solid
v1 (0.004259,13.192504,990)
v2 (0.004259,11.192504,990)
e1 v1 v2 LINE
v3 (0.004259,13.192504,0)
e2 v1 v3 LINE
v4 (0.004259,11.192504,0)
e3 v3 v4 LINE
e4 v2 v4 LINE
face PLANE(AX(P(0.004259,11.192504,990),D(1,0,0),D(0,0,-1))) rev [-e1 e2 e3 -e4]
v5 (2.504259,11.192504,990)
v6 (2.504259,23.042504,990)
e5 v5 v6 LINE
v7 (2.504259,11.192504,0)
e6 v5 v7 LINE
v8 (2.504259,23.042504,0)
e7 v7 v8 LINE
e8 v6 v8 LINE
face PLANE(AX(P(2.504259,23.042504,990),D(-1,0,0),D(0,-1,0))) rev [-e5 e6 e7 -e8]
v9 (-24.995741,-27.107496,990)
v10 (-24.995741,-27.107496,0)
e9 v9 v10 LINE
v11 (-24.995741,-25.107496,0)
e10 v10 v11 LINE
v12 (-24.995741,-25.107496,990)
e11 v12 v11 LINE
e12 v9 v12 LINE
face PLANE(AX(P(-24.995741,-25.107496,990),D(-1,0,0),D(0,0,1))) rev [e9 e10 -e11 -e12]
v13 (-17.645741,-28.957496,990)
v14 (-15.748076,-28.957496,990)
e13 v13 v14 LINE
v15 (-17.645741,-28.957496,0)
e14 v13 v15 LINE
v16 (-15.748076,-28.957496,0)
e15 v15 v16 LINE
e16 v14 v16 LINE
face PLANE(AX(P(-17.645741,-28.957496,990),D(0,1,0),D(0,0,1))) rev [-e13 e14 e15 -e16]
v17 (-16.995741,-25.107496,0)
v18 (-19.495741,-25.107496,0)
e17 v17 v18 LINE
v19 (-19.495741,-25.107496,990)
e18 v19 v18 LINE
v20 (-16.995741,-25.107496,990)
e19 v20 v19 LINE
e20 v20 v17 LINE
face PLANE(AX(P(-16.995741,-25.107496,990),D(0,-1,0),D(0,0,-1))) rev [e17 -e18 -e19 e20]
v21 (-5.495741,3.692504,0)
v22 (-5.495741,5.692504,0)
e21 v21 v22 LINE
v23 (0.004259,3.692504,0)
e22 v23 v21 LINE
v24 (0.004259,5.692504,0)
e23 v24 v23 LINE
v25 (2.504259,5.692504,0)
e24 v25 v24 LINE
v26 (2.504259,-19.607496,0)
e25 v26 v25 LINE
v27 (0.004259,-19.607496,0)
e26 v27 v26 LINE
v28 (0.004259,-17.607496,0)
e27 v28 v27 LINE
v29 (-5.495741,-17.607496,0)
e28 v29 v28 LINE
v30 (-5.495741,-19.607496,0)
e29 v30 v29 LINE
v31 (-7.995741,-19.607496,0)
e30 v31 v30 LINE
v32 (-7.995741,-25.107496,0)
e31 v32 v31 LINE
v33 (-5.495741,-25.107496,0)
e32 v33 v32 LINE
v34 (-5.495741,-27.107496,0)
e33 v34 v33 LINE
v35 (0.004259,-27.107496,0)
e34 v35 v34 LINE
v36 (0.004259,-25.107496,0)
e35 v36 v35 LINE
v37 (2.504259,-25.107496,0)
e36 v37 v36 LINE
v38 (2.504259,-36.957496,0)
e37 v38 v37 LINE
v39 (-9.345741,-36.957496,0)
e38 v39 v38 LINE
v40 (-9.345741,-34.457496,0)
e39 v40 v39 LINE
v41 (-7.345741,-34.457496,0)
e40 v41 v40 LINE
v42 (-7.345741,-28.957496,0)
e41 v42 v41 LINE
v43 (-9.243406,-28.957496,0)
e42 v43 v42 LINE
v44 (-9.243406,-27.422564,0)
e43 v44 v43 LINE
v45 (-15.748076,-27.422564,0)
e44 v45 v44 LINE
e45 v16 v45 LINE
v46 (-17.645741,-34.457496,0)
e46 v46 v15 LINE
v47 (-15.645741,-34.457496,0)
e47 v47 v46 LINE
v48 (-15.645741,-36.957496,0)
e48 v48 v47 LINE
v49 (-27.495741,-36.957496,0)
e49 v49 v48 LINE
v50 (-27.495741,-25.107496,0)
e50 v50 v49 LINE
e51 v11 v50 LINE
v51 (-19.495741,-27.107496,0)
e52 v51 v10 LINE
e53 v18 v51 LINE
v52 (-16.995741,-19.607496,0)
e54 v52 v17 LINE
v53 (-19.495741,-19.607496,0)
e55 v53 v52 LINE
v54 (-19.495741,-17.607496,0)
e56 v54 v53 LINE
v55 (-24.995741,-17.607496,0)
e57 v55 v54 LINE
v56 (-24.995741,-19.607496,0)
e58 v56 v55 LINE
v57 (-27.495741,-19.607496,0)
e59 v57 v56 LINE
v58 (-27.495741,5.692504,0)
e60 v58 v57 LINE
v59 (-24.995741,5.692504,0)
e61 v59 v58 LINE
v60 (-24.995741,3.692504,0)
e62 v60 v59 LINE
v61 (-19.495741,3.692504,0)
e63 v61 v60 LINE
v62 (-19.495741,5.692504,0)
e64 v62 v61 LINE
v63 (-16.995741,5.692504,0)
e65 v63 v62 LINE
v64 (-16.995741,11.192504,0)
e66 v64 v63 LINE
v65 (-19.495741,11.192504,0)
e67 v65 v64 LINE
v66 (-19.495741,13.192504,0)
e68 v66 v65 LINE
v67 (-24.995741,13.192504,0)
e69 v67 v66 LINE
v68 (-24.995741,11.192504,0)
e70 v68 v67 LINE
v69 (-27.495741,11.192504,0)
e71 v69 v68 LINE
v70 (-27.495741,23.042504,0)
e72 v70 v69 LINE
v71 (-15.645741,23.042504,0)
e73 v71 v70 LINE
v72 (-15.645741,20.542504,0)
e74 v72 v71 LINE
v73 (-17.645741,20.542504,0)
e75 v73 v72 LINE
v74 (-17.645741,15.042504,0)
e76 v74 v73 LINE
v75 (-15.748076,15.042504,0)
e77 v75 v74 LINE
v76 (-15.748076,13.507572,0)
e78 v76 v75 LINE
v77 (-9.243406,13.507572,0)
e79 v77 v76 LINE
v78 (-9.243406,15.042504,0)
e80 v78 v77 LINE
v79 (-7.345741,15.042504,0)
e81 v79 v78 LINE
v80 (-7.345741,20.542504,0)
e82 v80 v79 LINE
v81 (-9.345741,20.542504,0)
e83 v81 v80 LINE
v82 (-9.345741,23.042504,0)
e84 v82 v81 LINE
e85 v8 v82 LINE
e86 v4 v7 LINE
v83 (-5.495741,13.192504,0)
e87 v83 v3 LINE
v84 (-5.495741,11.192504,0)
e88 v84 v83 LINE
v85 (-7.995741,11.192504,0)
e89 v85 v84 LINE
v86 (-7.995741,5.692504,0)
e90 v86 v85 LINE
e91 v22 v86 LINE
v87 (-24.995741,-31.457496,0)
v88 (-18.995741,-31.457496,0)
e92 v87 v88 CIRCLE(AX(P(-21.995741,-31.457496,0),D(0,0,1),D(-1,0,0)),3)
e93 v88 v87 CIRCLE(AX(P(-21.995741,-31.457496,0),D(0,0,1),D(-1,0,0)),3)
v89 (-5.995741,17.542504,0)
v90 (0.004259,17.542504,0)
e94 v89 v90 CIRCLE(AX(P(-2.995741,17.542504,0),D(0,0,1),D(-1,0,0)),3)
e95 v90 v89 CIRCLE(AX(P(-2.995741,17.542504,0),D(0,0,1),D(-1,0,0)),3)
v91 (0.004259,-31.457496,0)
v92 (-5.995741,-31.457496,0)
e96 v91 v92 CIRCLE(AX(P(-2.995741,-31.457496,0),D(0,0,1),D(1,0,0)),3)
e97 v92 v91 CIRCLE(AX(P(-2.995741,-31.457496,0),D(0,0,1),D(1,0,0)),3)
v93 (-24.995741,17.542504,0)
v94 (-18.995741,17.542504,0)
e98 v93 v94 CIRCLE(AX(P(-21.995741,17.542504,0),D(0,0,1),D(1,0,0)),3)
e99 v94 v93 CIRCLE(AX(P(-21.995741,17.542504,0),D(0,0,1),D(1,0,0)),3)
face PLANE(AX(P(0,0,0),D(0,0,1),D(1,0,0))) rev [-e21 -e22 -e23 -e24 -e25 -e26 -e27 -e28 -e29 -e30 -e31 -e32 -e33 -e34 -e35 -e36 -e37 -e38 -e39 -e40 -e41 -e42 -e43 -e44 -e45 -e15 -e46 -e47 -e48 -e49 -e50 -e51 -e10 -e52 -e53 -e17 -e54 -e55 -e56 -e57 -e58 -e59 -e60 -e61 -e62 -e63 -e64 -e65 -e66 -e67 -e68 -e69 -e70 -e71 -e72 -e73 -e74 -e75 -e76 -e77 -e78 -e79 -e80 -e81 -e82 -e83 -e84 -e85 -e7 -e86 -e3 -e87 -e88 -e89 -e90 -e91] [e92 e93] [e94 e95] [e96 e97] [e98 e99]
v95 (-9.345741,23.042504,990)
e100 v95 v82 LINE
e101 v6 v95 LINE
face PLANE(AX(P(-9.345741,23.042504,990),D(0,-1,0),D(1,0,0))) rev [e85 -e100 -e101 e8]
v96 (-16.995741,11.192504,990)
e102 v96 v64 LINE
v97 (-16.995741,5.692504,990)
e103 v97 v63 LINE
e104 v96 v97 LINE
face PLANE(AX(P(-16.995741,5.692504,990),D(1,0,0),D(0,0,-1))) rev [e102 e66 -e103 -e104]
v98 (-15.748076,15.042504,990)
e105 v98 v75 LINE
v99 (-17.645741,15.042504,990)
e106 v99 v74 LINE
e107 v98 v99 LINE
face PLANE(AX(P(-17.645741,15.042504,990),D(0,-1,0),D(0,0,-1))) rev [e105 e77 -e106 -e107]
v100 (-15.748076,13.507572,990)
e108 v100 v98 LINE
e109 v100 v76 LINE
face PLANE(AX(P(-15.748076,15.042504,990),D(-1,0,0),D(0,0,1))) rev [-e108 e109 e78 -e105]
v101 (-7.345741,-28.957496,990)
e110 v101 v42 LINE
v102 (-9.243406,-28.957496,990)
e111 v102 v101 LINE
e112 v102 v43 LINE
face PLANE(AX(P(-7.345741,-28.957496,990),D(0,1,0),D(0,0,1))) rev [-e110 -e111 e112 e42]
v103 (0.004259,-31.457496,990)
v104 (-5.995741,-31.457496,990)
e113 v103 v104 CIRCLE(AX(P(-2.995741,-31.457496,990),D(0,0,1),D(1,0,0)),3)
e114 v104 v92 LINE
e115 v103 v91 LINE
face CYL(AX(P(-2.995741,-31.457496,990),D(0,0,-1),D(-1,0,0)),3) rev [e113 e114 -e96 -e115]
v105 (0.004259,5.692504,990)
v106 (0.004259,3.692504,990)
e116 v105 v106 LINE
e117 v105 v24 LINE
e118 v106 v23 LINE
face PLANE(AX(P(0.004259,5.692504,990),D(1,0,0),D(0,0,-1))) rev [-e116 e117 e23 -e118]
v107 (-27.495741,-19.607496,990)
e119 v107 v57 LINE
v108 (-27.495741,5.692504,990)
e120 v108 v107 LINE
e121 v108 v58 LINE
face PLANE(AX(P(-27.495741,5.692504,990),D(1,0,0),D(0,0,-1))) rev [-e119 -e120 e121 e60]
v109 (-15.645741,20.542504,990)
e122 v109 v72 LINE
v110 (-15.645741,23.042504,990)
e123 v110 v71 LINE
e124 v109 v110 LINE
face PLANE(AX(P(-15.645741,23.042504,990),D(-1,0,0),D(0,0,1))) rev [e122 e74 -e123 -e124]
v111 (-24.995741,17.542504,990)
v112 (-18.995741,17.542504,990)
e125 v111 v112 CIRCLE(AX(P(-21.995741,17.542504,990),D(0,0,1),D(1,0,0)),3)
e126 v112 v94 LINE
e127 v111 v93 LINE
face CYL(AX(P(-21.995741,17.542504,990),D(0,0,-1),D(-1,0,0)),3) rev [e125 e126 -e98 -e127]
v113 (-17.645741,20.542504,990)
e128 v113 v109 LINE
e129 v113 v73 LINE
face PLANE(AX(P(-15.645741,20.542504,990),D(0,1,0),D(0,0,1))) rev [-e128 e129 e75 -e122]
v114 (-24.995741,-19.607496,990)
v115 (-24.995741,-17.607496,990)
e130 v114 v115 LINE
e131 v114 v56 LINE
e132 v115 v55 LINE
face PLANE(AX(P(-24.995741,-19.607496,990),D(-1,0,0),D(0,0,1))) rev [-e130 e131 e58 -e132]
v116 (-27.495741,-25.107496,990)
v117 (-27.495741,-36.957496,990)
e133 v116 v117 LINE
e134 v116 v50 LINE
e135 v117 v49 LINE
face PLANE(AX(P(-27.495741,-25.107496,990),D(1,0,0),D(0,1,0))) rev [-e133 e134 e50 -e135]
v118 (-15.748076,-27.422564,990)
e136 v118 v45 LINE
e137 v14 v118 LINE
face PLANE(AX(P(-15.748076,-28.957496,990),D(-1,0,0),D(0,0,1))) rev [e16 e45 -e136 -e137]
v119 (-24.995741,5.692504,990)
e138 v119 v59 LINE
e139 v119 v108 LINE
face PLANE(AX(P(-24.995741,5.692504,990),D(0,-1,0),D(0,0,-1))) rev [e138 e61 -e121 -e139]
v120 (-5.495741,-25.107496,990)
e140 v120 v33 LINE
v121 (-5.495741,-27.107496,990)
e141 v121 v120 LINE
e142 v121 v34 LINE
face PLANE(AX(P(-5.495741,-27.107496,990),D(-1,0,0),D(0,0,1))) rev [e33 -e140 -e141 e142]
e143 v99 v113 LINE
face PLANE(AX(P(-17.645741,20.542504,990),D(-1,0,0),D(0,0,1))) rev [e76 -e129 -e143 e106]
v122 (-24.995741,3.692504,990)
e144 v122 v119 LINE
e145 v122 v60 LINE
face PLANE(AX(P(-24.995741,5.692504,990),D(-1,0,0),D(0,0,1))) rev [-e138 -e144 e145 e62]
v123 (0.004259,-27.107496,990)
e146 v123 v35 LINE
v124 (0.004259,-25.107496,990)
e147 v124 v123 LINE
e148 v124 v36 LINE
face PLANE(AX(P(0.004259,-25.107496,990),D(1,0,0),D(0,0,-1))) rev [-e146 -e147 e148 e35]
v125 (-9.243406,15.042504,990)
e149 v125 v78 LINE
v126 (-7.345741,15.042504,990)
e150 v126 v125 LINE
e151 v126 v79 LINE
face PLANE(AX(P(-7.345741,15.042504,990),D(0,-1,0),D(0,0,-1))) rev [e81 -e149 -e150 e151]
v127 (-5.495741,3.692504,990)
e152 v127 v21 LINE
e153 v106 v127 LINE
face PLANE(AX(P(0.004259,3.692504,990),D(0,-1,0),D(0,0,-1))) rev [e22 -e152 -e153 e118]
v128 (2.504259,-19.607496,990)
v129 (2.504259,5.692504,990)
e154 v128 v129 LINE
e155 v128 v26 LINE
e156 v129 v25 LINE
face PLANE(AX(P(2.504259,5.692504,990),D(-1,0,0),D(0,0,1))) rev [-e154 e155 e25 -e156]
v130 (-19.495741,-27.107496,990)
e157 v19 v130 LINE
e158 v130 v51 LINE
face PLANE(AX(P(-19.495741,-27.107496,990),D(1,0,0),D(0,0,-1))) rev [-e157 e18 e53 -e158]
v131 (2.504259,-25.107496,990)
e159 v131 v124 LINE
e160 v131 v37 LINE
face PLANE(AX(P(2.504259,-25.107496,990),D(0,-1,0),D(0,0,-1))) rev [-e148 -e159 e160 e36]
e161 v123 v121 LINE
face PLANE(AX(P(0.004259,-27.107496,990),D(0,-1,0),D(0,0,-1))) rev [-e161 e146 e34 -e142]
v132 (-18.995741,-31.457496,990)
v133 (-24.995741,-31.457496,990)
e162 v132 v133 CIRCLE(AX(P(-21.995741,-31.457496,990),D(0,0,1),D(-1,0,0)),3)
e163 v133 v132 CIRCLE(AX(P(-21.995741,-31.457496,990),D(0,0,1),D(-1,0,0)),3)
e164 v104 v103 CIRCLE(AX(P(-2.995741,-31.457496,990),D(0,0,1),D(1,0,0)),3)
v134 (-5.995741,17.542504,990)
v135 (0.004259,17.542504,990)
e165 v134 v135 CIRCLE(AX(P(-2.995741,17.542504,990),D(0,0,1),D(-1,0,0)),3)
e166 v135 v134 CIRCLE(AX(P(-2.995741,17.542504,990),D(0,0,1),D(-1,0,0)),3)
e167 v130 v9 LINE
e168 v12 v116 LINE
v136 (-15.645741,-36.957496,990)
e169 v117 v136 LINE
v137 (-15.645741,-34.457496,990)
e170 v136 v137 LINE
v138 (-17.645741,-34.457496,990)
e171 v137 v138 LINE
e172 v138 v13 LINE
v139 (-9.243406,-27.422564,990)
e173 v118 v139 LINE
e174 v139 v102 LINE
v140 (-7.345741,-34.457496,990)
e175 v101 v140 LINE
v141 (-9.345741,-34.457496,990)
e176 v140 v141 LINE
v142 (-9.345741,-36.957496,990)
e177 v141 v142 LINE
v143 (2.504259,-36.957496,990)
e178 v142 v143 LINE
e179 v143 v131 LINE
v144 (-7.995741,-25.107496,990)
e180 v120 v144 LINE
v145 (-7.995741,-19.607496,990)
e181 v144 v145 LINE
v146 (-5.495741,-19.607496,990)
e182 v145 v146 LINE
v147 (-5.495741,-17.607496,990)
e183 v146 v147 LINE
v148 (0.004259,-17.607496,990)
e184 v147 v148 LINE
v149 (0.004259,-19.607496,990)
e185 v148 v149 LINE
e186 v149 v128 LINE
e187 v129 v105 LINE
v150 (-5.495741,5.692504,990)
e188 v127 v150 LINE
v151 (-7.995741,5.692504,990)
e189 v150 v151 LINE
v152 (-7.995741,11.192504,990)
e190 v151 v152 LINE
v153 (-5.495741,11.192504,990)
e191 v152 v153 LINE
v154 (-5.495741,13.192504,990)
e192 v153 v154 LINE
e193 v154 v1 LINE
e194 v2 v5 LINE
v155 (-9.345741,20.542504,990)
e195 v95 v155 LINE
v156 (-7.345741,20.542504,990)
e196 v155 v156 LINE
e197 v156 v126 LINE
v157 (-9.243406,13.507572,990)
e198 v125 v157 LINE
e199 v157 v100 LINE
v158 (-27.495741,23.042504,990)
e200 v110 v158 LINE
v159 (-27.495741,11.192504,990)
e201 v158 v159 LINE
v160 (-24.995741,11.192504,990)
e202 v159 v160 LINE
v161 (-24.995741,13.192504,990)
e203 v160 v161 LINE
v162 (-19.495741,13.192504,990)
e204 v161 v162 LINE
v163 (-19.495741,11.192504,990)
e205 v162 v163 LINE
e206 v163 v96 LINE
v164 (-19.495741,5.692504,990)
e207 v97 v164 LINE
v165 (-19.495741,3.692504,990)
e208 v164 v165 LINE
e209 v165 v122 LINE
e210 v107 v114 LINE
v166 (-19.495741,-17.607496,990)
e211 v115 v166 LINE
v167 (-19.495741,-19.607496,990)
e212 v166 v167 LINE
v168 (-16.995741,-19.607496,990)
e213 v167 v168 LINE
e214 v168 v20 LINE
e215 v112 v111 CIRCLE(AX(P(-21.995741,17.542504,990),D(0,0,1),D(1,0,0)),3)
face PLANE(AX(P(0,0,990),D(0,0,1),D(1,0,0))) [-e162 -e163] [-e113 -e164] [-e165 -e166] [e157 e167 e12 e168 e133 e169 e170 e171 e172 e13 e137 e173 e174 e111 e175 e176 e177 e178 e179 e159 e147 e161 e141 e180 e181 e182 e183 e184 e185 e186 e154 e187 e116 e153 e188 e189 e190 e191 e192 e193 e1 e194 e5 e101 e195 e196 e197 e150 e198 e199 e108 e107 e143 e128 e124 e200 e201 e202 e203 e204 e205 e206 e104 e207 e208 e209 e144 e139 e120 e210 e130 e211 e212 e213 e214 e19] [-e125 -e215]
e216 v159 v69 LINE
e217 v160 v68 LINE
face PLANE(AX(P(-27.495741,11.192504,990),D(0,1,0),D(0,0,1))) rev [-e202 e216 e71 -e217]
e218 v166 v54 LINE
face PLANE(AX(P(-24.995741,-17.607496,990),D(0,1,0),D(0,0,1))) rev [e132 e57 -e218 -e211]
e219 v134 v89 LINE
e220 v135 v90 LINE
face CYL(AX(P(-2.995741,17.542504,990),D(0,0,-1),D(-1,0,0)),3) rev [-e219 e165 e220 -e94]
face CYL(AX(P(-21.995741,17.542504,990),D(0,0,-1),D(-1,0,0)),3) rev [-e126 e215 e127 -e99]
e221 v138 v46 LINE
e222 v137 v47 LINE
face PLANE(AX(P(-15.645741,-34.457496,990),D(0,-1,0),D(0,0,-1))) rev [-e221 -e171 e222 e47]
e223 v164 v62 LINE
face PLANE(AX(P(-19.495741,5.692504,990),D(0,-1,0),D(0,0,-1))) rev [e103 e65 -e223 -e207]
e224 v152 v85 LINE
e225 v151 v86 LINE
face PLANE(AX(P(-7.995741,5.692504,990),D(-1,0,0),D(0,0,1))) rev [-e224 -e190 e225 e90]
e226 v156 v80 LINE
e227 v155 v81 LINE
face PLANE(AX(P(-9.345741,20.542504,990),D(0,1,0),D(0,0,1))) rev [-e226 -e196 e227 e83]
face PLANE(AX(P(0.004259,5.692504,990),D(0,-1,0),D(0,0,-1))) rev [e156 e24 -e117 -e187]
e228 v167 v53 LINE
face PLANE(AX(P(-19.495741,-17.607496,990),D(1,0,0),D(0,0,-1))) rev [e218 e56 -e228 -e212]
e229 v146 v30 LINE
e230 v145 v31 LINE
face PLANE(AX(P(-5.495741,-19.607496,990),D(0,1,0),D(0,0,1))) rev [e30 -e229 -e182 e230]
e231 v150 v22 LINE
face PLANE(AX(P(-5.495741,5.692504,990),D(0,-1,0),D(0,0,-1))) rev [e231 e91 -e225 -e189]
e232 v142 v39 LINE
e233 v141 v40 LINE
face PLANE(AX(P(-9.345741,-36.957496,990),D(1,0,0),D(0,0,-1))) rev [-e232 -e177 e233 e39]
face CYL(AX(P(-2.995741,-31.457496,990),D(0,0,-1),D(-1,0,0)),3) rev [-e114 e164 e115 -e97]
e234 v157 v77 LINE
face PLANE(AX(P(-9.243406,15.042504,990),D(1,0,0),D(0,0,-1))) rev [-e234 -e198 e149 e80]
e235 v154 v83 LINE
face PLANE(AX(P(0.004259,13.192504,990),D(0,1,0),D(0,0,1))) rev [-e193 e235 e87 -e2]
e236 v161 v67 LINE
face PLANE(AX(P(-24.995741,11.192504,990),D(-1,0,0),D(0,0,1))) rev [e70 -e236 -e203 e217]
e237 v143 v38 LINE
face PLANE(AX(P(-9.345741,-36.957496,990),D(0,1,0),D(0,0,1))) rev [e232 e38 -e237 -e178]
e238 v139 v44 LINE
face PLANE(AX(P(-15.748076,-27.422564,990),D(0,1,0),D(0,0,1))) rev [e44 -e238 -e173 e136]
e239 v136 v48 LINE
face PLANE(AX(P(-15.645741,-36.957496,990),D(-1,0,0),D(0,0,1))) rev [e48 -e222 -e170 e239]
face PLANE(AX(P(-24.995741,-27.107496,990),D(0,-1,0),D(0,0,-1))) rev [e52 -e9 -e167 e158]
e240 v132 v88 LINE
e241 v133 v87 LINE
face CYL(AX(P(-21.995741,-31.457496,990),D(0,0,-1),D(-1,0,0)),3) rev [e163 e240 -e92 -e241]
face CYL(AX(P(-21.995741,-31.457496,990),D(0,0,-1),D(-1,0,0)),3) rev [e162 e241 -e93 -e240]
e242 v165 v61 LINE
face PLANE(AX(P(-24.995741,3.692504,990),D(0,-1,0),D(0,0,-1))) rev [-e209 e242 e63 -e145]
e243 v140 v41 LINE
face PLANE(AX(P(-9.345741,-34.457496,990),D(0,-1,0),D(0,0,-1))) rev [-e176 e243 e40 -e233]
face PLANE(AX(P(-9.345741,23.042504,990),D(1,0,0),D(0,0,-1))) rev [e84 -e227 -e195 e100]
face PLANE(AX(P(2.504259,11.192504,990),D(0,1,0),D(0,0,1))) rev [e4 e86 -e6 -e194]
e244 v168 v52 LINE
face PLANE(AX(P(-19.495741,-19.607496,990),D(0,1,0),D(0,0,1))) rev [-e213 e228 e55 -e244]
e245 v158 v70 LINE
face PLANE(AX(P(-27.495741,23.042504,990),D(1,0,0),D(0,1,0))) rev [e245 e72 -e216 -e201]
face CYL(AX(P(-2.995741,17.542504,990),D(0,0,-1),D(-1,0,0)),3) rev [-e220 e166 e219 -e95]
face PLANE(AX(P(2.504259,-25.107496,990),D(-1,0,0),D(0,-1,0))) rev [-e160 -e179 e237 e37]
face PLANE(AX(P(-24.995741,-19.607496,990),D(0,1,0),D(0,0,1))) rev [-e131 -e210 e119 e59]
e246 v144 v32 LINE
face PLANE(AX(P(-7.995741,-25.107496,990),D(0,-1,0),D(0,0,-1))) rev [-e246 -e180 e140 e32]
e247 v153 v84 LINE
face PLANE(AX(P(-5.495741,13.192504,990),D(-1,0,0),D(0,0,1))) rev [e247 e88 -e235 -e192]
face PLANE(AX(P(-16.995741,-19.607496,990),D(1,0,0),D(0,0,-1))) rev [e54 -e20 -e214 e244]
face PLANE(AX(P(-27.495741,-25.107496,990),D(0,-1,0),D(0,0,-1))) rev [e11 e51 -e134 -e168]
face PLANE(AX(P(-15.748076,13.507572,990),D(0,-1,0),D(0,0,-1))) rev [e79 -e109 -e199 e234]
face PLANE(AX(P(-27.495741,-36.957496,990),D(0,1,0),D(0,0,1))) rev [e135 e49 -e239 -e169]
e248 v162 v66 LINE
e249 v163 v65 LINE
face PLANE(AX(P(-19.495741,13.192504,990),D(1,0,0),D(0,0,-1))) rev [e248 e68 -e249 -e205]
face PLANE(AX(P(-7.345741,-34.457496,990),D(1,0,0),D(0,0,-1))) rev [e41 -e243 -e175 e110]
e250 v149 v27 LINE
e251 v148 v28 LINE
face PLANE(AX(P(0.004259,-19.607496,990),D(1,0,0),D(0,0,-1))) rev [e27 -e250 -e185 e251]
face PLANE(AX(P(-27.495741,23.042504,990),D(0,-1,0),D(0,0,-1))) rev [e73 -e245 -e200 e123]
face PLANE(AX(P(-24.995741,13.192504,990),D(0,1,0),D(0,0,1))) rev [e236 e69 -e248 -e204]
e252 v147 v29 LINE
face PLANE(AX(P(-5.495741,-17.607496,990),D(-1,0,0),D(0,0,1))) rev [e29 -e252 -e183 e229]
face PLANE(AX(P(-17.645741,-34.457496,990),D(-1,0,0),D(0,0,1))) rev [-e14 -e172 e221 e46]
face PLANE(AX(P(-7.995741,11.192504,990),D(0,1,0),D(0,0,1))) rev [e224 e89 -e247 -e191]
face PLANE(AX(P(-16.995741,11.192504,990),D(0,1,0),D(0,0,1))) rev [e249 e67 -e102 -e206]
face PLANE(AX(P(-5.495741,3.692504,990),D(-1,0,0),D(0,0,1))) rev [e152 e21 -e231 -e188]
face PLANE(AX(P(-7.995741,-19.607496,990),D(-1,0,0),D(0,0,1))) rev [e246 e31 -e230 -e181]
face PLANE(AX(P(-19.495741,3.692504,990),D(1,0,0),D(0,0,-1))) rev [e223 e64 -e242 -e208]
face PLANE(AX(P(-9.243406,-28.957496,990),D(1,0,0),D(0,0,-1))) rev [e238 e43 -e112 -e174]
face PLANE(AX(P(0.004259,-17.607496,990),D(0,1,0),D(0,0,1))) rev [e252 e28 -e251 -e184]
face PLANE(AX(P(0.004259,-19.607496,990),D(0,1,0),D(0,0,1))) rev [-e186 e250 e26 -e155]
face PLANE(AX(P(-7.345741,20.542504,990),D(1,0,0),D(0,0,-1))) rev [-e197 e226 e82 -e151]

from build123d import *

# Parameters (mm, degrees)
SKETCH_1_R      = 3
EXTRUDE_1_DEPTH = 990


with BuildPart() as part:
    # 草图1 → 凸台-拉伸1 (new body)
    with BuildSketch(Plane.XY):
        Polygon((-27.495741056, 11.192504259), (-24.995741056, 11.192504259), (-24.995741056, 13.192504259), (-19.495741056, 13.192504259), (-19.495741056, 11.192504259), (-16.995741056, 11.192504259), (-16.995741056, 5.692504259), (-19.495741056, 5.692504259), (-19.495741056, 3.692504259), (-24.995741056, 3.692504259), (-24.995741056, 5.692504259), (-27.495741056, 5.692504259), (-27.495741056, -19.607495741), (-24.995741056, -19.607495741), (-24.995741056, -17.607495741), (-19.495741056, -17.607495741), (-19.495741056, -19.607495741), (-16.995741056, -19.607495741), (-16.995741056, -25.107495741), (-19.495741056, -25.107495741), (-19.495741056, -27.107495741), (-24.995741056, -27.107495741), (-24.995741056, -25.107495741), (-27.495741056, -25.107495741), (-27.495741056, -36.957495741), (-15.645741056, -36.957495741), (-15.645741056, -34.457495741), (-17.645741056, -34.457495741), (-17.645741056, -28.957495741), (-15.748076247, -28.957495741), (-15.748076247, -27.422563567), (-9.243405866, -27.422563567), (-9.243405866, -28.957495741), (-7.345741056, -28.957495741), (-7.345741056, -34.457495741), (-9.345741056, -34.457495741), (-9.345741056, -36.957495741), (2.504258944, -36.957495741), (2.504258944, -25.107495741), (0.004258944, -25.107495741), (0.004258944, -27.107495741), (-5.495741056, -27.107495741), (-5.495741056, -25.107495741), (-7.995741056, -25.107495741), (-7.995741056, -19.607495741), (-5.495741056, -19.607495741), (-5.495741056, -17.607495741), (0.004258944, -17.607495741), (0.004258944, -19.607495741), (2.504258944, -19.607495741), (2.504258944, 5.692504259), (0.004258944, 5.692504259), (0.004258944, 3.692504259), (-5.495741056, 3.692504259), (-5.495741056, 5.692504259), (-7.995741056, 5.692504259), (-7.995741056, 11.192504259), (-5.495741056, 11.192504259), (-5.495741056, 13.192504259), (0.004258944, 13.192504259), (0.004258944, 11.192504259), (2.504258944, 11.192504259), (2.504258944, 23.042504259), (-9.345741056, 23.042504259), (-9.345741056, 20.542504259), (-7.345741056, 20.542504259), (-7.345741056, 15.042504259), (-9.243405866, 15.042504259), (-9.243405866, 13.507572085), (-15.748076247, 13.507572085), (-15.748076247, 15.042504259), (-17.645741056, 15.042504259), (-17.645741056, 20.542504259), (-15.645741056, 20.542504259), (-15.645741056, 23.042504259), (-27.495741056, 23.042504259), align=None)
        with Locations((-21.995741056, 17.542504259)):
            Circle(SKETCH_1_R, mode=Mode.SUBTRACT)
        with Locations(Location((-2.995741056, 17.542504259, 0), (0, 0, 180))):
            Circle(SKETCH_1_R, mode=Mode.SUBTRACT)
        with Locations((-2.995741056, -31.457495741)):
            Circle(SKETCH_1_R, mode=Mode.SUBTRACT)
        with Locations(Location((-21.995741056, -31.457495741, 0), (0, 0, 180))):
            Circle(SKETCH_1_R, mode=Mode.SUBTRACT)
    extrude(amount=EXTRUDE_1_DEPTH)


solid = part.part
